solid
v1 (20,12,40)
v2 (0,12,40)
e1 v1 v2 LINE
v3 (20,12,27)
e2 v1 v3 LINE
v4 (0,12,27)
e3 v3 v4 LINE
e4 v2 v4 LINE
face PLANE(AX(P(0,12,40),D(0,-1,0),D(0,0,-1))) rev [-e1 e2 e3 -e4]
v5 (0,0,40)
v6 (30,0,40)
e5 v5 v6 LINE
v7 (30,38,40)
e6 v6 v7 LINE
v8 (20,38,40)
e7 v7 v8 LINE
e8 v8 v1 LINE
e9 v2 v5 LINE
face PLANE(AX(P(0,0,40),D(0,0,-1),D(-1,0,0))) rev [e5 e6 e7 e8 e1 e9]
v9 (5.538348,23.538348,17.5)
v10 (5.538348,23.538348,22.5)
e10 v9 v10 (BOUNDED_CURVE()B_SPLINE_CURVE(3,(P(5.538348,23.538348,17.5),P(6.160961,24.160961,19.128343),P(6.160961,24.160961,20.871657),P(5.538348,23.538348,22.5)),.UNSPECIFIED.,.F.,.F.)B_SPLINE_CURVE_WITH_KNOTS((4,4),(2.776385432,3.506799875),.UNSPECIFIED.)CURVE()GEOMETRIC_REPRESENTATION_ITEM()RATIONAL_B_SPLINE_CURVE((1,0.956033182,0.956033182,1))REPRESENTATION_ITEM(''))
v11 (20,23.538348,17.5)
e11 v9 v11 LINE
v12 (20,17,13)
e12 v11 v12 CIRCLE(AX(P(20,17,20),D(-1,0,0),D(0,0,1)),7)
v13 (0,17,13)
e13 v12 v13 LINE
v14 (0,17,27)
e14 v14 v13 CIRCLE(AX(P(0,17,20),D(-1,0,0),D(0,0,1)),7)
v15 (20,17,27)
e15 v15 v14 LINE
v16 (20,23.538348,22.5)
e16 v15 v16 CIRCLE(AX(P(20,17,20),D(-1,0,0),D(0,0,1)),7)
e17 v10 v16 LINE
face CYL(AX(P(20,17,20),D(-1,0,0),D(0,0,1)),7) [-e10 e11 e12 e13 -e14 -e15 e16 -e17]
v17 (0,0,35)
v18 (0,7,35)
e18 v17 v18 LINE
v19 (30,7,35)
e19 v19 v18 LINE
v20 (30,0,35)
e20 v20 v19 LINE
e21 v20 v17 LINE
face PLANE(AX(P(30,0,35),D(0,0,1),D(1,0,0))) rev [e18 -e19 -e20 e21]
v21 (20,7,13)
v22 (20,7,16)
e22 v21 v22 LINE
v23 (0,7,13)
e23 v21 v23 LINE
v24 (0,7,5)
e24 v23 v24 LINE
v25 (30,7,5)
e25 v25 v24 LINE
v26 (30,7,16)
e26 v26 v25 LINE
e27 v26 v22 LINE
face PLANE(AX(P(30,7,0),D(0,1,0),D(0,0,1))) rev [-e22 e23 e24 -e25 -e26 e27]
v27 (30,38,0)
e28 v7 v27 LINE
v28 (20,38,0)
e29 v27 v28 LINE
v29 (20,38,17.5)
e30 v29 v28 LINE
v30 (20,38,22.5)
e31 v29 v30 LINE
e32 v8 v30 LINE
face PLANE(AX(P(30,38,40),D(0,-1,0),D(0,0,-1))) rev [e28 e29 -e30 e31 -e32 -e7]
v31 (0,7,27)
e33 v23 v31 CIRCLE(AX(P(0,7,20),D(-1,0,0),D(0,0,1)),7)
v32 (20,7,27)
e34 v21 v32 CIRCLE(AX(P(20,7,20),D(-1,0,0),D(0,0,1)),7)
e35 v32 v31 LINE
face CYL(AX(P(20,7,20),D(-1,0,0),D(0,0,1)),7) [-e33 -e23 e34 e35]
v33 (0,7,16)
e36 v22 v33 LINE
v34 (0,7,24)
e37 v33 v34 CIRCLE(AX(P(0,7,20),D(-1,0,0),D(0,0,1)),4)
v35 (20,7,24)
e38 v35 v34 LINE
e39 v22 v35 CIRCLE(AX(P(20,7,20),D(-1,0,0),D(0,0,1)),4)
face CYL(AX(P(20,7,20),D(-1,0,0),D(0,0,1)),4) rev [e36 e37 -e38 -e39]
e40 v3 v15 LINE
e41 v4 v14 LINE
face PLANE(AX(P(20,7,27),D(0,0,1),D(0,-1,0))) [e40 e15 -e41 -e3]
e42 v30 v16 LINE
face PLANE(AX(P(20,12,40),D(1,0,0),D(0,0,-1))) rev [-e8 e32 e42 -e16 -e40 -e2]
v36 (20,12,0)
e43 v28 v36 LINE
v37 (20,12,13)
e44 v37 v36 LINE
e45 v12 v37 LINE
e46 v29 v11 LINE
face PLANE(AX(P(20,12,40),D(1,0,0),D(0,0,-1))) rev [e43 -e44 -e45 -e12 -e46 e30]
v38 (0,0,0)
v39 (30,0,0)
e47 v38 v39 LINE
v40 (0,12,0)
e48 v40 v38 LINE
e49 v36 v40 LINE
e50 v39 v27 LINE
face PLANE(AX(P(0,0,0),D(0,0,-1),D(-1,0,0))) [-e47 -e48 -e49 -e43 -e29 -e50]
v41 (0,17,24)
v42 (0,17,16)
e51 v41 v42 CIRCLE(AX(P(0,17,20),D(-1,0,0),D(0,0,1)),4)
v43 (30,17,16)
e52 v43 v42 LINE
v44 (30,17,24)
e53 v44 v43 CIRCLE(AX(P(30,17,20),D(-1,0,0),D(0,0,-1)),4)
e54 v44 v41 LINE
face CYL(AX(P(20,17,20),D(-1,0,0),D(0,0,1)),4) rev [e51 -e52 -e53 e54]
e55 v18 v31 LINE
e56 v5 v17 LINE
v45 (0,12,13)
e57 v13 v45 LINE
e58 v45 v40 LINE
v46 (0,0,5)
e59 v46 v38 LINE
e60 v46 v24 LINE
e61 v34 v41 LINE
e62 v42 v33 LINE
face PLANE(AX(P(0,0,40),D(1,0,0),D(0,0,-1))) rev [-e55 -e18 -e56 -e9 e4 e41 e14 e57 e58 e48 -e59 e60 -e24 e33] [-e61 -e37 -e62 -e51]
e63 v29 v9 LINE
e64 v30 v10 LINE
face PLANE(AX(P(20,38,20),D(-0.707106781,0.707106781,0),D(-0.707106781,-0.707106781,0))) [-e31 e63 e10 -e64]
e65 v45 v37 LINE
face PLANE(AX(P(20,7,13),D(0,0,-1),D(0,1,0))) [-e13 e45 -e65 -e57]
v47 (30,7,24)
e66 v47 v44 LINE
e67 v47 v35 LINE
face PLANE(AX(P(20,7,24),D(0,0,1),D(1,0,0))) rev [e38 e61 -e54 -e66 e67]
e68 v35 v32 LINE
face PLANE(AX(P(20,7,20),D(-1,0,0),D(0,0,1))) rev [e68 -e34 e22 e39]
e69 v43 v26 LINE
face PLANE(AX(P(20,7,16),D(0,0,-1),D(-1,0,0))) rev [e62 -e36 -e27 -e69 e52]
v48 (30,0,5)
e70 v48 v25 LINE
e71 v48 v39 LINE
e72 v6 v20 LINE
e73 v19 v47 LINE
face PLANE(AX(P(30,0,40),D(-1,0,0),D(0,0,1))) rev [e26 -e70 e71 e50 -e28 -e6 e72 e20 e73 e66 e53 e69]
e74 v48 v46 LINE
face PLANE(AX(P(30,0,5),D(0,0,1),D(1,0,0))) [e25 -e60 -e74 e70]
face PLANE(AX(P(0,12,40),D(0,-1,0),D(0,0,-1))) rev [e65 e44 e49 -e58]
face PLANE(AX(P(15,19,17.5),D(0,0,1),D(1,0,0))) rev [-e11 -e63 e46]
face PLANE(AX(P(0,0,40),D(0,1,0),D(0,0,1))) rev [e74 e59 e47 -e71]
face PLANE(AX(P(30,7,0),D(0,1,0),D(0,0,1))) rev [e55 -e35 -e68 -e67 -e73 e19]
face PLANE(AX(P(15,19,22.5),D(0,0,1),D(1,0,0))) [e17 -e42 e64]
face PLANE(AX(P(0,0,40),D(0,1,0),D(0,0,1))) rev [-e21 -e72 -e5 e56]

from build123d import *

# Parameters (mm, degrees)
BRACKET_BODY_DEPTH        = 40
BASE_NOTCH_SKETCH_W       = 30
BASE_NOTCH_SKETCH_H       = 7
BASE_NOTCH_CUT_DEPTH      = 63.801273872
CYLINDRICAL_BOSS_DEPTH    = 20
UPRIGHT_OPENING_SKETCH_W  = 8
UPRIGHT_OPENING_SKETCH_H  = 5
UPRIGHT_OPENING_CUT_DEPTH = 20
ARCHED_RELIEF_CUT_DEPTH   = 59.685603004
SUPPORT_RIB_45DEG_REACH   = 54.383
SUPPORT_RIB_SKETCH_WALL_W = 126.565396702
SUPPORT_RIB_SKETCH_WALL_H = 5


with BuildPart() as part:
    # Bracket Profile Sketch → Bracket Body (new body)
    with BuildSketch(Plane.XY):
        Polygon((0, 0), (30, 0), (30, 38), (20, 38), (20, 12), (0, 12), align=None)
    extrude(amount=BRACKET_BODY_DEPTH)

    # Base Notch Sketch → Base Notch Cut (cut, through all)
    with BuildSketch(Plane.ZY):
        with Locations((20, 3.5)):
            Rectangle(BASE_NOTCH_SKETCH_W, BASE_NOTCH_SKETCH_H)
    extrude(amount=-BASE_NOTCH_CUT_DEPTH, mode=Mode.SUBTRACT)

    # Cylindrical Boss Sketch → Cylindrical Boss (add)
    with BuildSketch(Plane.ZY):
        with BuildLine():
            Line((13, 7), (13, 17))
            ThreePointArc((13, 17), (20, 24), (27, 17))
            Line((27, 17), (27, 7))
            ThreePointArc((27, 7), (20, 0), (13, 7))
        make_face()
        with BuildLine():
            Line((16, 7), (16, 17))
            ThreePointArc((16, 17), (20, 21), (24, 17))
            Line((24, 17), (24, 7))
            ThreePointArc((24, 7), (20, 3), (16, 7))
        make_face(mode=Mode.SUBTRACT)
    extrude(amount=-CYLINDRICAL_BOSS_DEPTH)

    # Upright Opening Sketch → Upright Opening Cut (cut)
    with BuildSketch(Plane.ZY):
        with Locations((20, 9.5)):
            Rectangle(UPRIGHT_OPENING_SKETCH_W, UPRIGHT_OPENING_SKETCH_H)
    extrude(amount=-UPRIGHT_OPENING_CUT_DEPTH, mode=Mode.SUBTRACT)

    # Arched Relief Sketch → Arched Relief Cut (cut, through all)
    with BuildSketch(Plane.ZY.offset(-20)):
        with BuildLine():
            Line((16, 17), (16, 7))
            Line((16, 7), (24, 7))
            Line((24, 7), (24, 17))
            ThreePointArc((24, 17), (20, 21), (16, 17))
        make_face()
    extrude(amount=-ARCHED_RELIEF_CUT_DEPTH, mode=Mode.SUBTRACT)

    # Support Rib Sketch wall → Support Rib 45deg (add, up to next)
    with BuildSketch(Plane(origin=(13, 31, 20), x_dir=(-0.707106781187, -0.707106781187, 0), z_dir=(0.707106781187, -0.707106781187, 0)), mode=Mode.PRIVATE) as support_rib_45deg_sk1:
        Rectangle(SUPPORT_RIB_SKETCH_WALL_W, SUPPORT_RIB_SKETCH_WALL_H)
    support_rib_45deg_tool1 = extrude(support_rib_45deg_sk1.sketch, amount=SUPPORT_RIB_45DEG_REACH, mode=Mode.PRIVATE) - part.part
    add(support_rib_45deg_tool1.solids().sort_by_distance((13, 31, 20))[0])


solid = part.part
